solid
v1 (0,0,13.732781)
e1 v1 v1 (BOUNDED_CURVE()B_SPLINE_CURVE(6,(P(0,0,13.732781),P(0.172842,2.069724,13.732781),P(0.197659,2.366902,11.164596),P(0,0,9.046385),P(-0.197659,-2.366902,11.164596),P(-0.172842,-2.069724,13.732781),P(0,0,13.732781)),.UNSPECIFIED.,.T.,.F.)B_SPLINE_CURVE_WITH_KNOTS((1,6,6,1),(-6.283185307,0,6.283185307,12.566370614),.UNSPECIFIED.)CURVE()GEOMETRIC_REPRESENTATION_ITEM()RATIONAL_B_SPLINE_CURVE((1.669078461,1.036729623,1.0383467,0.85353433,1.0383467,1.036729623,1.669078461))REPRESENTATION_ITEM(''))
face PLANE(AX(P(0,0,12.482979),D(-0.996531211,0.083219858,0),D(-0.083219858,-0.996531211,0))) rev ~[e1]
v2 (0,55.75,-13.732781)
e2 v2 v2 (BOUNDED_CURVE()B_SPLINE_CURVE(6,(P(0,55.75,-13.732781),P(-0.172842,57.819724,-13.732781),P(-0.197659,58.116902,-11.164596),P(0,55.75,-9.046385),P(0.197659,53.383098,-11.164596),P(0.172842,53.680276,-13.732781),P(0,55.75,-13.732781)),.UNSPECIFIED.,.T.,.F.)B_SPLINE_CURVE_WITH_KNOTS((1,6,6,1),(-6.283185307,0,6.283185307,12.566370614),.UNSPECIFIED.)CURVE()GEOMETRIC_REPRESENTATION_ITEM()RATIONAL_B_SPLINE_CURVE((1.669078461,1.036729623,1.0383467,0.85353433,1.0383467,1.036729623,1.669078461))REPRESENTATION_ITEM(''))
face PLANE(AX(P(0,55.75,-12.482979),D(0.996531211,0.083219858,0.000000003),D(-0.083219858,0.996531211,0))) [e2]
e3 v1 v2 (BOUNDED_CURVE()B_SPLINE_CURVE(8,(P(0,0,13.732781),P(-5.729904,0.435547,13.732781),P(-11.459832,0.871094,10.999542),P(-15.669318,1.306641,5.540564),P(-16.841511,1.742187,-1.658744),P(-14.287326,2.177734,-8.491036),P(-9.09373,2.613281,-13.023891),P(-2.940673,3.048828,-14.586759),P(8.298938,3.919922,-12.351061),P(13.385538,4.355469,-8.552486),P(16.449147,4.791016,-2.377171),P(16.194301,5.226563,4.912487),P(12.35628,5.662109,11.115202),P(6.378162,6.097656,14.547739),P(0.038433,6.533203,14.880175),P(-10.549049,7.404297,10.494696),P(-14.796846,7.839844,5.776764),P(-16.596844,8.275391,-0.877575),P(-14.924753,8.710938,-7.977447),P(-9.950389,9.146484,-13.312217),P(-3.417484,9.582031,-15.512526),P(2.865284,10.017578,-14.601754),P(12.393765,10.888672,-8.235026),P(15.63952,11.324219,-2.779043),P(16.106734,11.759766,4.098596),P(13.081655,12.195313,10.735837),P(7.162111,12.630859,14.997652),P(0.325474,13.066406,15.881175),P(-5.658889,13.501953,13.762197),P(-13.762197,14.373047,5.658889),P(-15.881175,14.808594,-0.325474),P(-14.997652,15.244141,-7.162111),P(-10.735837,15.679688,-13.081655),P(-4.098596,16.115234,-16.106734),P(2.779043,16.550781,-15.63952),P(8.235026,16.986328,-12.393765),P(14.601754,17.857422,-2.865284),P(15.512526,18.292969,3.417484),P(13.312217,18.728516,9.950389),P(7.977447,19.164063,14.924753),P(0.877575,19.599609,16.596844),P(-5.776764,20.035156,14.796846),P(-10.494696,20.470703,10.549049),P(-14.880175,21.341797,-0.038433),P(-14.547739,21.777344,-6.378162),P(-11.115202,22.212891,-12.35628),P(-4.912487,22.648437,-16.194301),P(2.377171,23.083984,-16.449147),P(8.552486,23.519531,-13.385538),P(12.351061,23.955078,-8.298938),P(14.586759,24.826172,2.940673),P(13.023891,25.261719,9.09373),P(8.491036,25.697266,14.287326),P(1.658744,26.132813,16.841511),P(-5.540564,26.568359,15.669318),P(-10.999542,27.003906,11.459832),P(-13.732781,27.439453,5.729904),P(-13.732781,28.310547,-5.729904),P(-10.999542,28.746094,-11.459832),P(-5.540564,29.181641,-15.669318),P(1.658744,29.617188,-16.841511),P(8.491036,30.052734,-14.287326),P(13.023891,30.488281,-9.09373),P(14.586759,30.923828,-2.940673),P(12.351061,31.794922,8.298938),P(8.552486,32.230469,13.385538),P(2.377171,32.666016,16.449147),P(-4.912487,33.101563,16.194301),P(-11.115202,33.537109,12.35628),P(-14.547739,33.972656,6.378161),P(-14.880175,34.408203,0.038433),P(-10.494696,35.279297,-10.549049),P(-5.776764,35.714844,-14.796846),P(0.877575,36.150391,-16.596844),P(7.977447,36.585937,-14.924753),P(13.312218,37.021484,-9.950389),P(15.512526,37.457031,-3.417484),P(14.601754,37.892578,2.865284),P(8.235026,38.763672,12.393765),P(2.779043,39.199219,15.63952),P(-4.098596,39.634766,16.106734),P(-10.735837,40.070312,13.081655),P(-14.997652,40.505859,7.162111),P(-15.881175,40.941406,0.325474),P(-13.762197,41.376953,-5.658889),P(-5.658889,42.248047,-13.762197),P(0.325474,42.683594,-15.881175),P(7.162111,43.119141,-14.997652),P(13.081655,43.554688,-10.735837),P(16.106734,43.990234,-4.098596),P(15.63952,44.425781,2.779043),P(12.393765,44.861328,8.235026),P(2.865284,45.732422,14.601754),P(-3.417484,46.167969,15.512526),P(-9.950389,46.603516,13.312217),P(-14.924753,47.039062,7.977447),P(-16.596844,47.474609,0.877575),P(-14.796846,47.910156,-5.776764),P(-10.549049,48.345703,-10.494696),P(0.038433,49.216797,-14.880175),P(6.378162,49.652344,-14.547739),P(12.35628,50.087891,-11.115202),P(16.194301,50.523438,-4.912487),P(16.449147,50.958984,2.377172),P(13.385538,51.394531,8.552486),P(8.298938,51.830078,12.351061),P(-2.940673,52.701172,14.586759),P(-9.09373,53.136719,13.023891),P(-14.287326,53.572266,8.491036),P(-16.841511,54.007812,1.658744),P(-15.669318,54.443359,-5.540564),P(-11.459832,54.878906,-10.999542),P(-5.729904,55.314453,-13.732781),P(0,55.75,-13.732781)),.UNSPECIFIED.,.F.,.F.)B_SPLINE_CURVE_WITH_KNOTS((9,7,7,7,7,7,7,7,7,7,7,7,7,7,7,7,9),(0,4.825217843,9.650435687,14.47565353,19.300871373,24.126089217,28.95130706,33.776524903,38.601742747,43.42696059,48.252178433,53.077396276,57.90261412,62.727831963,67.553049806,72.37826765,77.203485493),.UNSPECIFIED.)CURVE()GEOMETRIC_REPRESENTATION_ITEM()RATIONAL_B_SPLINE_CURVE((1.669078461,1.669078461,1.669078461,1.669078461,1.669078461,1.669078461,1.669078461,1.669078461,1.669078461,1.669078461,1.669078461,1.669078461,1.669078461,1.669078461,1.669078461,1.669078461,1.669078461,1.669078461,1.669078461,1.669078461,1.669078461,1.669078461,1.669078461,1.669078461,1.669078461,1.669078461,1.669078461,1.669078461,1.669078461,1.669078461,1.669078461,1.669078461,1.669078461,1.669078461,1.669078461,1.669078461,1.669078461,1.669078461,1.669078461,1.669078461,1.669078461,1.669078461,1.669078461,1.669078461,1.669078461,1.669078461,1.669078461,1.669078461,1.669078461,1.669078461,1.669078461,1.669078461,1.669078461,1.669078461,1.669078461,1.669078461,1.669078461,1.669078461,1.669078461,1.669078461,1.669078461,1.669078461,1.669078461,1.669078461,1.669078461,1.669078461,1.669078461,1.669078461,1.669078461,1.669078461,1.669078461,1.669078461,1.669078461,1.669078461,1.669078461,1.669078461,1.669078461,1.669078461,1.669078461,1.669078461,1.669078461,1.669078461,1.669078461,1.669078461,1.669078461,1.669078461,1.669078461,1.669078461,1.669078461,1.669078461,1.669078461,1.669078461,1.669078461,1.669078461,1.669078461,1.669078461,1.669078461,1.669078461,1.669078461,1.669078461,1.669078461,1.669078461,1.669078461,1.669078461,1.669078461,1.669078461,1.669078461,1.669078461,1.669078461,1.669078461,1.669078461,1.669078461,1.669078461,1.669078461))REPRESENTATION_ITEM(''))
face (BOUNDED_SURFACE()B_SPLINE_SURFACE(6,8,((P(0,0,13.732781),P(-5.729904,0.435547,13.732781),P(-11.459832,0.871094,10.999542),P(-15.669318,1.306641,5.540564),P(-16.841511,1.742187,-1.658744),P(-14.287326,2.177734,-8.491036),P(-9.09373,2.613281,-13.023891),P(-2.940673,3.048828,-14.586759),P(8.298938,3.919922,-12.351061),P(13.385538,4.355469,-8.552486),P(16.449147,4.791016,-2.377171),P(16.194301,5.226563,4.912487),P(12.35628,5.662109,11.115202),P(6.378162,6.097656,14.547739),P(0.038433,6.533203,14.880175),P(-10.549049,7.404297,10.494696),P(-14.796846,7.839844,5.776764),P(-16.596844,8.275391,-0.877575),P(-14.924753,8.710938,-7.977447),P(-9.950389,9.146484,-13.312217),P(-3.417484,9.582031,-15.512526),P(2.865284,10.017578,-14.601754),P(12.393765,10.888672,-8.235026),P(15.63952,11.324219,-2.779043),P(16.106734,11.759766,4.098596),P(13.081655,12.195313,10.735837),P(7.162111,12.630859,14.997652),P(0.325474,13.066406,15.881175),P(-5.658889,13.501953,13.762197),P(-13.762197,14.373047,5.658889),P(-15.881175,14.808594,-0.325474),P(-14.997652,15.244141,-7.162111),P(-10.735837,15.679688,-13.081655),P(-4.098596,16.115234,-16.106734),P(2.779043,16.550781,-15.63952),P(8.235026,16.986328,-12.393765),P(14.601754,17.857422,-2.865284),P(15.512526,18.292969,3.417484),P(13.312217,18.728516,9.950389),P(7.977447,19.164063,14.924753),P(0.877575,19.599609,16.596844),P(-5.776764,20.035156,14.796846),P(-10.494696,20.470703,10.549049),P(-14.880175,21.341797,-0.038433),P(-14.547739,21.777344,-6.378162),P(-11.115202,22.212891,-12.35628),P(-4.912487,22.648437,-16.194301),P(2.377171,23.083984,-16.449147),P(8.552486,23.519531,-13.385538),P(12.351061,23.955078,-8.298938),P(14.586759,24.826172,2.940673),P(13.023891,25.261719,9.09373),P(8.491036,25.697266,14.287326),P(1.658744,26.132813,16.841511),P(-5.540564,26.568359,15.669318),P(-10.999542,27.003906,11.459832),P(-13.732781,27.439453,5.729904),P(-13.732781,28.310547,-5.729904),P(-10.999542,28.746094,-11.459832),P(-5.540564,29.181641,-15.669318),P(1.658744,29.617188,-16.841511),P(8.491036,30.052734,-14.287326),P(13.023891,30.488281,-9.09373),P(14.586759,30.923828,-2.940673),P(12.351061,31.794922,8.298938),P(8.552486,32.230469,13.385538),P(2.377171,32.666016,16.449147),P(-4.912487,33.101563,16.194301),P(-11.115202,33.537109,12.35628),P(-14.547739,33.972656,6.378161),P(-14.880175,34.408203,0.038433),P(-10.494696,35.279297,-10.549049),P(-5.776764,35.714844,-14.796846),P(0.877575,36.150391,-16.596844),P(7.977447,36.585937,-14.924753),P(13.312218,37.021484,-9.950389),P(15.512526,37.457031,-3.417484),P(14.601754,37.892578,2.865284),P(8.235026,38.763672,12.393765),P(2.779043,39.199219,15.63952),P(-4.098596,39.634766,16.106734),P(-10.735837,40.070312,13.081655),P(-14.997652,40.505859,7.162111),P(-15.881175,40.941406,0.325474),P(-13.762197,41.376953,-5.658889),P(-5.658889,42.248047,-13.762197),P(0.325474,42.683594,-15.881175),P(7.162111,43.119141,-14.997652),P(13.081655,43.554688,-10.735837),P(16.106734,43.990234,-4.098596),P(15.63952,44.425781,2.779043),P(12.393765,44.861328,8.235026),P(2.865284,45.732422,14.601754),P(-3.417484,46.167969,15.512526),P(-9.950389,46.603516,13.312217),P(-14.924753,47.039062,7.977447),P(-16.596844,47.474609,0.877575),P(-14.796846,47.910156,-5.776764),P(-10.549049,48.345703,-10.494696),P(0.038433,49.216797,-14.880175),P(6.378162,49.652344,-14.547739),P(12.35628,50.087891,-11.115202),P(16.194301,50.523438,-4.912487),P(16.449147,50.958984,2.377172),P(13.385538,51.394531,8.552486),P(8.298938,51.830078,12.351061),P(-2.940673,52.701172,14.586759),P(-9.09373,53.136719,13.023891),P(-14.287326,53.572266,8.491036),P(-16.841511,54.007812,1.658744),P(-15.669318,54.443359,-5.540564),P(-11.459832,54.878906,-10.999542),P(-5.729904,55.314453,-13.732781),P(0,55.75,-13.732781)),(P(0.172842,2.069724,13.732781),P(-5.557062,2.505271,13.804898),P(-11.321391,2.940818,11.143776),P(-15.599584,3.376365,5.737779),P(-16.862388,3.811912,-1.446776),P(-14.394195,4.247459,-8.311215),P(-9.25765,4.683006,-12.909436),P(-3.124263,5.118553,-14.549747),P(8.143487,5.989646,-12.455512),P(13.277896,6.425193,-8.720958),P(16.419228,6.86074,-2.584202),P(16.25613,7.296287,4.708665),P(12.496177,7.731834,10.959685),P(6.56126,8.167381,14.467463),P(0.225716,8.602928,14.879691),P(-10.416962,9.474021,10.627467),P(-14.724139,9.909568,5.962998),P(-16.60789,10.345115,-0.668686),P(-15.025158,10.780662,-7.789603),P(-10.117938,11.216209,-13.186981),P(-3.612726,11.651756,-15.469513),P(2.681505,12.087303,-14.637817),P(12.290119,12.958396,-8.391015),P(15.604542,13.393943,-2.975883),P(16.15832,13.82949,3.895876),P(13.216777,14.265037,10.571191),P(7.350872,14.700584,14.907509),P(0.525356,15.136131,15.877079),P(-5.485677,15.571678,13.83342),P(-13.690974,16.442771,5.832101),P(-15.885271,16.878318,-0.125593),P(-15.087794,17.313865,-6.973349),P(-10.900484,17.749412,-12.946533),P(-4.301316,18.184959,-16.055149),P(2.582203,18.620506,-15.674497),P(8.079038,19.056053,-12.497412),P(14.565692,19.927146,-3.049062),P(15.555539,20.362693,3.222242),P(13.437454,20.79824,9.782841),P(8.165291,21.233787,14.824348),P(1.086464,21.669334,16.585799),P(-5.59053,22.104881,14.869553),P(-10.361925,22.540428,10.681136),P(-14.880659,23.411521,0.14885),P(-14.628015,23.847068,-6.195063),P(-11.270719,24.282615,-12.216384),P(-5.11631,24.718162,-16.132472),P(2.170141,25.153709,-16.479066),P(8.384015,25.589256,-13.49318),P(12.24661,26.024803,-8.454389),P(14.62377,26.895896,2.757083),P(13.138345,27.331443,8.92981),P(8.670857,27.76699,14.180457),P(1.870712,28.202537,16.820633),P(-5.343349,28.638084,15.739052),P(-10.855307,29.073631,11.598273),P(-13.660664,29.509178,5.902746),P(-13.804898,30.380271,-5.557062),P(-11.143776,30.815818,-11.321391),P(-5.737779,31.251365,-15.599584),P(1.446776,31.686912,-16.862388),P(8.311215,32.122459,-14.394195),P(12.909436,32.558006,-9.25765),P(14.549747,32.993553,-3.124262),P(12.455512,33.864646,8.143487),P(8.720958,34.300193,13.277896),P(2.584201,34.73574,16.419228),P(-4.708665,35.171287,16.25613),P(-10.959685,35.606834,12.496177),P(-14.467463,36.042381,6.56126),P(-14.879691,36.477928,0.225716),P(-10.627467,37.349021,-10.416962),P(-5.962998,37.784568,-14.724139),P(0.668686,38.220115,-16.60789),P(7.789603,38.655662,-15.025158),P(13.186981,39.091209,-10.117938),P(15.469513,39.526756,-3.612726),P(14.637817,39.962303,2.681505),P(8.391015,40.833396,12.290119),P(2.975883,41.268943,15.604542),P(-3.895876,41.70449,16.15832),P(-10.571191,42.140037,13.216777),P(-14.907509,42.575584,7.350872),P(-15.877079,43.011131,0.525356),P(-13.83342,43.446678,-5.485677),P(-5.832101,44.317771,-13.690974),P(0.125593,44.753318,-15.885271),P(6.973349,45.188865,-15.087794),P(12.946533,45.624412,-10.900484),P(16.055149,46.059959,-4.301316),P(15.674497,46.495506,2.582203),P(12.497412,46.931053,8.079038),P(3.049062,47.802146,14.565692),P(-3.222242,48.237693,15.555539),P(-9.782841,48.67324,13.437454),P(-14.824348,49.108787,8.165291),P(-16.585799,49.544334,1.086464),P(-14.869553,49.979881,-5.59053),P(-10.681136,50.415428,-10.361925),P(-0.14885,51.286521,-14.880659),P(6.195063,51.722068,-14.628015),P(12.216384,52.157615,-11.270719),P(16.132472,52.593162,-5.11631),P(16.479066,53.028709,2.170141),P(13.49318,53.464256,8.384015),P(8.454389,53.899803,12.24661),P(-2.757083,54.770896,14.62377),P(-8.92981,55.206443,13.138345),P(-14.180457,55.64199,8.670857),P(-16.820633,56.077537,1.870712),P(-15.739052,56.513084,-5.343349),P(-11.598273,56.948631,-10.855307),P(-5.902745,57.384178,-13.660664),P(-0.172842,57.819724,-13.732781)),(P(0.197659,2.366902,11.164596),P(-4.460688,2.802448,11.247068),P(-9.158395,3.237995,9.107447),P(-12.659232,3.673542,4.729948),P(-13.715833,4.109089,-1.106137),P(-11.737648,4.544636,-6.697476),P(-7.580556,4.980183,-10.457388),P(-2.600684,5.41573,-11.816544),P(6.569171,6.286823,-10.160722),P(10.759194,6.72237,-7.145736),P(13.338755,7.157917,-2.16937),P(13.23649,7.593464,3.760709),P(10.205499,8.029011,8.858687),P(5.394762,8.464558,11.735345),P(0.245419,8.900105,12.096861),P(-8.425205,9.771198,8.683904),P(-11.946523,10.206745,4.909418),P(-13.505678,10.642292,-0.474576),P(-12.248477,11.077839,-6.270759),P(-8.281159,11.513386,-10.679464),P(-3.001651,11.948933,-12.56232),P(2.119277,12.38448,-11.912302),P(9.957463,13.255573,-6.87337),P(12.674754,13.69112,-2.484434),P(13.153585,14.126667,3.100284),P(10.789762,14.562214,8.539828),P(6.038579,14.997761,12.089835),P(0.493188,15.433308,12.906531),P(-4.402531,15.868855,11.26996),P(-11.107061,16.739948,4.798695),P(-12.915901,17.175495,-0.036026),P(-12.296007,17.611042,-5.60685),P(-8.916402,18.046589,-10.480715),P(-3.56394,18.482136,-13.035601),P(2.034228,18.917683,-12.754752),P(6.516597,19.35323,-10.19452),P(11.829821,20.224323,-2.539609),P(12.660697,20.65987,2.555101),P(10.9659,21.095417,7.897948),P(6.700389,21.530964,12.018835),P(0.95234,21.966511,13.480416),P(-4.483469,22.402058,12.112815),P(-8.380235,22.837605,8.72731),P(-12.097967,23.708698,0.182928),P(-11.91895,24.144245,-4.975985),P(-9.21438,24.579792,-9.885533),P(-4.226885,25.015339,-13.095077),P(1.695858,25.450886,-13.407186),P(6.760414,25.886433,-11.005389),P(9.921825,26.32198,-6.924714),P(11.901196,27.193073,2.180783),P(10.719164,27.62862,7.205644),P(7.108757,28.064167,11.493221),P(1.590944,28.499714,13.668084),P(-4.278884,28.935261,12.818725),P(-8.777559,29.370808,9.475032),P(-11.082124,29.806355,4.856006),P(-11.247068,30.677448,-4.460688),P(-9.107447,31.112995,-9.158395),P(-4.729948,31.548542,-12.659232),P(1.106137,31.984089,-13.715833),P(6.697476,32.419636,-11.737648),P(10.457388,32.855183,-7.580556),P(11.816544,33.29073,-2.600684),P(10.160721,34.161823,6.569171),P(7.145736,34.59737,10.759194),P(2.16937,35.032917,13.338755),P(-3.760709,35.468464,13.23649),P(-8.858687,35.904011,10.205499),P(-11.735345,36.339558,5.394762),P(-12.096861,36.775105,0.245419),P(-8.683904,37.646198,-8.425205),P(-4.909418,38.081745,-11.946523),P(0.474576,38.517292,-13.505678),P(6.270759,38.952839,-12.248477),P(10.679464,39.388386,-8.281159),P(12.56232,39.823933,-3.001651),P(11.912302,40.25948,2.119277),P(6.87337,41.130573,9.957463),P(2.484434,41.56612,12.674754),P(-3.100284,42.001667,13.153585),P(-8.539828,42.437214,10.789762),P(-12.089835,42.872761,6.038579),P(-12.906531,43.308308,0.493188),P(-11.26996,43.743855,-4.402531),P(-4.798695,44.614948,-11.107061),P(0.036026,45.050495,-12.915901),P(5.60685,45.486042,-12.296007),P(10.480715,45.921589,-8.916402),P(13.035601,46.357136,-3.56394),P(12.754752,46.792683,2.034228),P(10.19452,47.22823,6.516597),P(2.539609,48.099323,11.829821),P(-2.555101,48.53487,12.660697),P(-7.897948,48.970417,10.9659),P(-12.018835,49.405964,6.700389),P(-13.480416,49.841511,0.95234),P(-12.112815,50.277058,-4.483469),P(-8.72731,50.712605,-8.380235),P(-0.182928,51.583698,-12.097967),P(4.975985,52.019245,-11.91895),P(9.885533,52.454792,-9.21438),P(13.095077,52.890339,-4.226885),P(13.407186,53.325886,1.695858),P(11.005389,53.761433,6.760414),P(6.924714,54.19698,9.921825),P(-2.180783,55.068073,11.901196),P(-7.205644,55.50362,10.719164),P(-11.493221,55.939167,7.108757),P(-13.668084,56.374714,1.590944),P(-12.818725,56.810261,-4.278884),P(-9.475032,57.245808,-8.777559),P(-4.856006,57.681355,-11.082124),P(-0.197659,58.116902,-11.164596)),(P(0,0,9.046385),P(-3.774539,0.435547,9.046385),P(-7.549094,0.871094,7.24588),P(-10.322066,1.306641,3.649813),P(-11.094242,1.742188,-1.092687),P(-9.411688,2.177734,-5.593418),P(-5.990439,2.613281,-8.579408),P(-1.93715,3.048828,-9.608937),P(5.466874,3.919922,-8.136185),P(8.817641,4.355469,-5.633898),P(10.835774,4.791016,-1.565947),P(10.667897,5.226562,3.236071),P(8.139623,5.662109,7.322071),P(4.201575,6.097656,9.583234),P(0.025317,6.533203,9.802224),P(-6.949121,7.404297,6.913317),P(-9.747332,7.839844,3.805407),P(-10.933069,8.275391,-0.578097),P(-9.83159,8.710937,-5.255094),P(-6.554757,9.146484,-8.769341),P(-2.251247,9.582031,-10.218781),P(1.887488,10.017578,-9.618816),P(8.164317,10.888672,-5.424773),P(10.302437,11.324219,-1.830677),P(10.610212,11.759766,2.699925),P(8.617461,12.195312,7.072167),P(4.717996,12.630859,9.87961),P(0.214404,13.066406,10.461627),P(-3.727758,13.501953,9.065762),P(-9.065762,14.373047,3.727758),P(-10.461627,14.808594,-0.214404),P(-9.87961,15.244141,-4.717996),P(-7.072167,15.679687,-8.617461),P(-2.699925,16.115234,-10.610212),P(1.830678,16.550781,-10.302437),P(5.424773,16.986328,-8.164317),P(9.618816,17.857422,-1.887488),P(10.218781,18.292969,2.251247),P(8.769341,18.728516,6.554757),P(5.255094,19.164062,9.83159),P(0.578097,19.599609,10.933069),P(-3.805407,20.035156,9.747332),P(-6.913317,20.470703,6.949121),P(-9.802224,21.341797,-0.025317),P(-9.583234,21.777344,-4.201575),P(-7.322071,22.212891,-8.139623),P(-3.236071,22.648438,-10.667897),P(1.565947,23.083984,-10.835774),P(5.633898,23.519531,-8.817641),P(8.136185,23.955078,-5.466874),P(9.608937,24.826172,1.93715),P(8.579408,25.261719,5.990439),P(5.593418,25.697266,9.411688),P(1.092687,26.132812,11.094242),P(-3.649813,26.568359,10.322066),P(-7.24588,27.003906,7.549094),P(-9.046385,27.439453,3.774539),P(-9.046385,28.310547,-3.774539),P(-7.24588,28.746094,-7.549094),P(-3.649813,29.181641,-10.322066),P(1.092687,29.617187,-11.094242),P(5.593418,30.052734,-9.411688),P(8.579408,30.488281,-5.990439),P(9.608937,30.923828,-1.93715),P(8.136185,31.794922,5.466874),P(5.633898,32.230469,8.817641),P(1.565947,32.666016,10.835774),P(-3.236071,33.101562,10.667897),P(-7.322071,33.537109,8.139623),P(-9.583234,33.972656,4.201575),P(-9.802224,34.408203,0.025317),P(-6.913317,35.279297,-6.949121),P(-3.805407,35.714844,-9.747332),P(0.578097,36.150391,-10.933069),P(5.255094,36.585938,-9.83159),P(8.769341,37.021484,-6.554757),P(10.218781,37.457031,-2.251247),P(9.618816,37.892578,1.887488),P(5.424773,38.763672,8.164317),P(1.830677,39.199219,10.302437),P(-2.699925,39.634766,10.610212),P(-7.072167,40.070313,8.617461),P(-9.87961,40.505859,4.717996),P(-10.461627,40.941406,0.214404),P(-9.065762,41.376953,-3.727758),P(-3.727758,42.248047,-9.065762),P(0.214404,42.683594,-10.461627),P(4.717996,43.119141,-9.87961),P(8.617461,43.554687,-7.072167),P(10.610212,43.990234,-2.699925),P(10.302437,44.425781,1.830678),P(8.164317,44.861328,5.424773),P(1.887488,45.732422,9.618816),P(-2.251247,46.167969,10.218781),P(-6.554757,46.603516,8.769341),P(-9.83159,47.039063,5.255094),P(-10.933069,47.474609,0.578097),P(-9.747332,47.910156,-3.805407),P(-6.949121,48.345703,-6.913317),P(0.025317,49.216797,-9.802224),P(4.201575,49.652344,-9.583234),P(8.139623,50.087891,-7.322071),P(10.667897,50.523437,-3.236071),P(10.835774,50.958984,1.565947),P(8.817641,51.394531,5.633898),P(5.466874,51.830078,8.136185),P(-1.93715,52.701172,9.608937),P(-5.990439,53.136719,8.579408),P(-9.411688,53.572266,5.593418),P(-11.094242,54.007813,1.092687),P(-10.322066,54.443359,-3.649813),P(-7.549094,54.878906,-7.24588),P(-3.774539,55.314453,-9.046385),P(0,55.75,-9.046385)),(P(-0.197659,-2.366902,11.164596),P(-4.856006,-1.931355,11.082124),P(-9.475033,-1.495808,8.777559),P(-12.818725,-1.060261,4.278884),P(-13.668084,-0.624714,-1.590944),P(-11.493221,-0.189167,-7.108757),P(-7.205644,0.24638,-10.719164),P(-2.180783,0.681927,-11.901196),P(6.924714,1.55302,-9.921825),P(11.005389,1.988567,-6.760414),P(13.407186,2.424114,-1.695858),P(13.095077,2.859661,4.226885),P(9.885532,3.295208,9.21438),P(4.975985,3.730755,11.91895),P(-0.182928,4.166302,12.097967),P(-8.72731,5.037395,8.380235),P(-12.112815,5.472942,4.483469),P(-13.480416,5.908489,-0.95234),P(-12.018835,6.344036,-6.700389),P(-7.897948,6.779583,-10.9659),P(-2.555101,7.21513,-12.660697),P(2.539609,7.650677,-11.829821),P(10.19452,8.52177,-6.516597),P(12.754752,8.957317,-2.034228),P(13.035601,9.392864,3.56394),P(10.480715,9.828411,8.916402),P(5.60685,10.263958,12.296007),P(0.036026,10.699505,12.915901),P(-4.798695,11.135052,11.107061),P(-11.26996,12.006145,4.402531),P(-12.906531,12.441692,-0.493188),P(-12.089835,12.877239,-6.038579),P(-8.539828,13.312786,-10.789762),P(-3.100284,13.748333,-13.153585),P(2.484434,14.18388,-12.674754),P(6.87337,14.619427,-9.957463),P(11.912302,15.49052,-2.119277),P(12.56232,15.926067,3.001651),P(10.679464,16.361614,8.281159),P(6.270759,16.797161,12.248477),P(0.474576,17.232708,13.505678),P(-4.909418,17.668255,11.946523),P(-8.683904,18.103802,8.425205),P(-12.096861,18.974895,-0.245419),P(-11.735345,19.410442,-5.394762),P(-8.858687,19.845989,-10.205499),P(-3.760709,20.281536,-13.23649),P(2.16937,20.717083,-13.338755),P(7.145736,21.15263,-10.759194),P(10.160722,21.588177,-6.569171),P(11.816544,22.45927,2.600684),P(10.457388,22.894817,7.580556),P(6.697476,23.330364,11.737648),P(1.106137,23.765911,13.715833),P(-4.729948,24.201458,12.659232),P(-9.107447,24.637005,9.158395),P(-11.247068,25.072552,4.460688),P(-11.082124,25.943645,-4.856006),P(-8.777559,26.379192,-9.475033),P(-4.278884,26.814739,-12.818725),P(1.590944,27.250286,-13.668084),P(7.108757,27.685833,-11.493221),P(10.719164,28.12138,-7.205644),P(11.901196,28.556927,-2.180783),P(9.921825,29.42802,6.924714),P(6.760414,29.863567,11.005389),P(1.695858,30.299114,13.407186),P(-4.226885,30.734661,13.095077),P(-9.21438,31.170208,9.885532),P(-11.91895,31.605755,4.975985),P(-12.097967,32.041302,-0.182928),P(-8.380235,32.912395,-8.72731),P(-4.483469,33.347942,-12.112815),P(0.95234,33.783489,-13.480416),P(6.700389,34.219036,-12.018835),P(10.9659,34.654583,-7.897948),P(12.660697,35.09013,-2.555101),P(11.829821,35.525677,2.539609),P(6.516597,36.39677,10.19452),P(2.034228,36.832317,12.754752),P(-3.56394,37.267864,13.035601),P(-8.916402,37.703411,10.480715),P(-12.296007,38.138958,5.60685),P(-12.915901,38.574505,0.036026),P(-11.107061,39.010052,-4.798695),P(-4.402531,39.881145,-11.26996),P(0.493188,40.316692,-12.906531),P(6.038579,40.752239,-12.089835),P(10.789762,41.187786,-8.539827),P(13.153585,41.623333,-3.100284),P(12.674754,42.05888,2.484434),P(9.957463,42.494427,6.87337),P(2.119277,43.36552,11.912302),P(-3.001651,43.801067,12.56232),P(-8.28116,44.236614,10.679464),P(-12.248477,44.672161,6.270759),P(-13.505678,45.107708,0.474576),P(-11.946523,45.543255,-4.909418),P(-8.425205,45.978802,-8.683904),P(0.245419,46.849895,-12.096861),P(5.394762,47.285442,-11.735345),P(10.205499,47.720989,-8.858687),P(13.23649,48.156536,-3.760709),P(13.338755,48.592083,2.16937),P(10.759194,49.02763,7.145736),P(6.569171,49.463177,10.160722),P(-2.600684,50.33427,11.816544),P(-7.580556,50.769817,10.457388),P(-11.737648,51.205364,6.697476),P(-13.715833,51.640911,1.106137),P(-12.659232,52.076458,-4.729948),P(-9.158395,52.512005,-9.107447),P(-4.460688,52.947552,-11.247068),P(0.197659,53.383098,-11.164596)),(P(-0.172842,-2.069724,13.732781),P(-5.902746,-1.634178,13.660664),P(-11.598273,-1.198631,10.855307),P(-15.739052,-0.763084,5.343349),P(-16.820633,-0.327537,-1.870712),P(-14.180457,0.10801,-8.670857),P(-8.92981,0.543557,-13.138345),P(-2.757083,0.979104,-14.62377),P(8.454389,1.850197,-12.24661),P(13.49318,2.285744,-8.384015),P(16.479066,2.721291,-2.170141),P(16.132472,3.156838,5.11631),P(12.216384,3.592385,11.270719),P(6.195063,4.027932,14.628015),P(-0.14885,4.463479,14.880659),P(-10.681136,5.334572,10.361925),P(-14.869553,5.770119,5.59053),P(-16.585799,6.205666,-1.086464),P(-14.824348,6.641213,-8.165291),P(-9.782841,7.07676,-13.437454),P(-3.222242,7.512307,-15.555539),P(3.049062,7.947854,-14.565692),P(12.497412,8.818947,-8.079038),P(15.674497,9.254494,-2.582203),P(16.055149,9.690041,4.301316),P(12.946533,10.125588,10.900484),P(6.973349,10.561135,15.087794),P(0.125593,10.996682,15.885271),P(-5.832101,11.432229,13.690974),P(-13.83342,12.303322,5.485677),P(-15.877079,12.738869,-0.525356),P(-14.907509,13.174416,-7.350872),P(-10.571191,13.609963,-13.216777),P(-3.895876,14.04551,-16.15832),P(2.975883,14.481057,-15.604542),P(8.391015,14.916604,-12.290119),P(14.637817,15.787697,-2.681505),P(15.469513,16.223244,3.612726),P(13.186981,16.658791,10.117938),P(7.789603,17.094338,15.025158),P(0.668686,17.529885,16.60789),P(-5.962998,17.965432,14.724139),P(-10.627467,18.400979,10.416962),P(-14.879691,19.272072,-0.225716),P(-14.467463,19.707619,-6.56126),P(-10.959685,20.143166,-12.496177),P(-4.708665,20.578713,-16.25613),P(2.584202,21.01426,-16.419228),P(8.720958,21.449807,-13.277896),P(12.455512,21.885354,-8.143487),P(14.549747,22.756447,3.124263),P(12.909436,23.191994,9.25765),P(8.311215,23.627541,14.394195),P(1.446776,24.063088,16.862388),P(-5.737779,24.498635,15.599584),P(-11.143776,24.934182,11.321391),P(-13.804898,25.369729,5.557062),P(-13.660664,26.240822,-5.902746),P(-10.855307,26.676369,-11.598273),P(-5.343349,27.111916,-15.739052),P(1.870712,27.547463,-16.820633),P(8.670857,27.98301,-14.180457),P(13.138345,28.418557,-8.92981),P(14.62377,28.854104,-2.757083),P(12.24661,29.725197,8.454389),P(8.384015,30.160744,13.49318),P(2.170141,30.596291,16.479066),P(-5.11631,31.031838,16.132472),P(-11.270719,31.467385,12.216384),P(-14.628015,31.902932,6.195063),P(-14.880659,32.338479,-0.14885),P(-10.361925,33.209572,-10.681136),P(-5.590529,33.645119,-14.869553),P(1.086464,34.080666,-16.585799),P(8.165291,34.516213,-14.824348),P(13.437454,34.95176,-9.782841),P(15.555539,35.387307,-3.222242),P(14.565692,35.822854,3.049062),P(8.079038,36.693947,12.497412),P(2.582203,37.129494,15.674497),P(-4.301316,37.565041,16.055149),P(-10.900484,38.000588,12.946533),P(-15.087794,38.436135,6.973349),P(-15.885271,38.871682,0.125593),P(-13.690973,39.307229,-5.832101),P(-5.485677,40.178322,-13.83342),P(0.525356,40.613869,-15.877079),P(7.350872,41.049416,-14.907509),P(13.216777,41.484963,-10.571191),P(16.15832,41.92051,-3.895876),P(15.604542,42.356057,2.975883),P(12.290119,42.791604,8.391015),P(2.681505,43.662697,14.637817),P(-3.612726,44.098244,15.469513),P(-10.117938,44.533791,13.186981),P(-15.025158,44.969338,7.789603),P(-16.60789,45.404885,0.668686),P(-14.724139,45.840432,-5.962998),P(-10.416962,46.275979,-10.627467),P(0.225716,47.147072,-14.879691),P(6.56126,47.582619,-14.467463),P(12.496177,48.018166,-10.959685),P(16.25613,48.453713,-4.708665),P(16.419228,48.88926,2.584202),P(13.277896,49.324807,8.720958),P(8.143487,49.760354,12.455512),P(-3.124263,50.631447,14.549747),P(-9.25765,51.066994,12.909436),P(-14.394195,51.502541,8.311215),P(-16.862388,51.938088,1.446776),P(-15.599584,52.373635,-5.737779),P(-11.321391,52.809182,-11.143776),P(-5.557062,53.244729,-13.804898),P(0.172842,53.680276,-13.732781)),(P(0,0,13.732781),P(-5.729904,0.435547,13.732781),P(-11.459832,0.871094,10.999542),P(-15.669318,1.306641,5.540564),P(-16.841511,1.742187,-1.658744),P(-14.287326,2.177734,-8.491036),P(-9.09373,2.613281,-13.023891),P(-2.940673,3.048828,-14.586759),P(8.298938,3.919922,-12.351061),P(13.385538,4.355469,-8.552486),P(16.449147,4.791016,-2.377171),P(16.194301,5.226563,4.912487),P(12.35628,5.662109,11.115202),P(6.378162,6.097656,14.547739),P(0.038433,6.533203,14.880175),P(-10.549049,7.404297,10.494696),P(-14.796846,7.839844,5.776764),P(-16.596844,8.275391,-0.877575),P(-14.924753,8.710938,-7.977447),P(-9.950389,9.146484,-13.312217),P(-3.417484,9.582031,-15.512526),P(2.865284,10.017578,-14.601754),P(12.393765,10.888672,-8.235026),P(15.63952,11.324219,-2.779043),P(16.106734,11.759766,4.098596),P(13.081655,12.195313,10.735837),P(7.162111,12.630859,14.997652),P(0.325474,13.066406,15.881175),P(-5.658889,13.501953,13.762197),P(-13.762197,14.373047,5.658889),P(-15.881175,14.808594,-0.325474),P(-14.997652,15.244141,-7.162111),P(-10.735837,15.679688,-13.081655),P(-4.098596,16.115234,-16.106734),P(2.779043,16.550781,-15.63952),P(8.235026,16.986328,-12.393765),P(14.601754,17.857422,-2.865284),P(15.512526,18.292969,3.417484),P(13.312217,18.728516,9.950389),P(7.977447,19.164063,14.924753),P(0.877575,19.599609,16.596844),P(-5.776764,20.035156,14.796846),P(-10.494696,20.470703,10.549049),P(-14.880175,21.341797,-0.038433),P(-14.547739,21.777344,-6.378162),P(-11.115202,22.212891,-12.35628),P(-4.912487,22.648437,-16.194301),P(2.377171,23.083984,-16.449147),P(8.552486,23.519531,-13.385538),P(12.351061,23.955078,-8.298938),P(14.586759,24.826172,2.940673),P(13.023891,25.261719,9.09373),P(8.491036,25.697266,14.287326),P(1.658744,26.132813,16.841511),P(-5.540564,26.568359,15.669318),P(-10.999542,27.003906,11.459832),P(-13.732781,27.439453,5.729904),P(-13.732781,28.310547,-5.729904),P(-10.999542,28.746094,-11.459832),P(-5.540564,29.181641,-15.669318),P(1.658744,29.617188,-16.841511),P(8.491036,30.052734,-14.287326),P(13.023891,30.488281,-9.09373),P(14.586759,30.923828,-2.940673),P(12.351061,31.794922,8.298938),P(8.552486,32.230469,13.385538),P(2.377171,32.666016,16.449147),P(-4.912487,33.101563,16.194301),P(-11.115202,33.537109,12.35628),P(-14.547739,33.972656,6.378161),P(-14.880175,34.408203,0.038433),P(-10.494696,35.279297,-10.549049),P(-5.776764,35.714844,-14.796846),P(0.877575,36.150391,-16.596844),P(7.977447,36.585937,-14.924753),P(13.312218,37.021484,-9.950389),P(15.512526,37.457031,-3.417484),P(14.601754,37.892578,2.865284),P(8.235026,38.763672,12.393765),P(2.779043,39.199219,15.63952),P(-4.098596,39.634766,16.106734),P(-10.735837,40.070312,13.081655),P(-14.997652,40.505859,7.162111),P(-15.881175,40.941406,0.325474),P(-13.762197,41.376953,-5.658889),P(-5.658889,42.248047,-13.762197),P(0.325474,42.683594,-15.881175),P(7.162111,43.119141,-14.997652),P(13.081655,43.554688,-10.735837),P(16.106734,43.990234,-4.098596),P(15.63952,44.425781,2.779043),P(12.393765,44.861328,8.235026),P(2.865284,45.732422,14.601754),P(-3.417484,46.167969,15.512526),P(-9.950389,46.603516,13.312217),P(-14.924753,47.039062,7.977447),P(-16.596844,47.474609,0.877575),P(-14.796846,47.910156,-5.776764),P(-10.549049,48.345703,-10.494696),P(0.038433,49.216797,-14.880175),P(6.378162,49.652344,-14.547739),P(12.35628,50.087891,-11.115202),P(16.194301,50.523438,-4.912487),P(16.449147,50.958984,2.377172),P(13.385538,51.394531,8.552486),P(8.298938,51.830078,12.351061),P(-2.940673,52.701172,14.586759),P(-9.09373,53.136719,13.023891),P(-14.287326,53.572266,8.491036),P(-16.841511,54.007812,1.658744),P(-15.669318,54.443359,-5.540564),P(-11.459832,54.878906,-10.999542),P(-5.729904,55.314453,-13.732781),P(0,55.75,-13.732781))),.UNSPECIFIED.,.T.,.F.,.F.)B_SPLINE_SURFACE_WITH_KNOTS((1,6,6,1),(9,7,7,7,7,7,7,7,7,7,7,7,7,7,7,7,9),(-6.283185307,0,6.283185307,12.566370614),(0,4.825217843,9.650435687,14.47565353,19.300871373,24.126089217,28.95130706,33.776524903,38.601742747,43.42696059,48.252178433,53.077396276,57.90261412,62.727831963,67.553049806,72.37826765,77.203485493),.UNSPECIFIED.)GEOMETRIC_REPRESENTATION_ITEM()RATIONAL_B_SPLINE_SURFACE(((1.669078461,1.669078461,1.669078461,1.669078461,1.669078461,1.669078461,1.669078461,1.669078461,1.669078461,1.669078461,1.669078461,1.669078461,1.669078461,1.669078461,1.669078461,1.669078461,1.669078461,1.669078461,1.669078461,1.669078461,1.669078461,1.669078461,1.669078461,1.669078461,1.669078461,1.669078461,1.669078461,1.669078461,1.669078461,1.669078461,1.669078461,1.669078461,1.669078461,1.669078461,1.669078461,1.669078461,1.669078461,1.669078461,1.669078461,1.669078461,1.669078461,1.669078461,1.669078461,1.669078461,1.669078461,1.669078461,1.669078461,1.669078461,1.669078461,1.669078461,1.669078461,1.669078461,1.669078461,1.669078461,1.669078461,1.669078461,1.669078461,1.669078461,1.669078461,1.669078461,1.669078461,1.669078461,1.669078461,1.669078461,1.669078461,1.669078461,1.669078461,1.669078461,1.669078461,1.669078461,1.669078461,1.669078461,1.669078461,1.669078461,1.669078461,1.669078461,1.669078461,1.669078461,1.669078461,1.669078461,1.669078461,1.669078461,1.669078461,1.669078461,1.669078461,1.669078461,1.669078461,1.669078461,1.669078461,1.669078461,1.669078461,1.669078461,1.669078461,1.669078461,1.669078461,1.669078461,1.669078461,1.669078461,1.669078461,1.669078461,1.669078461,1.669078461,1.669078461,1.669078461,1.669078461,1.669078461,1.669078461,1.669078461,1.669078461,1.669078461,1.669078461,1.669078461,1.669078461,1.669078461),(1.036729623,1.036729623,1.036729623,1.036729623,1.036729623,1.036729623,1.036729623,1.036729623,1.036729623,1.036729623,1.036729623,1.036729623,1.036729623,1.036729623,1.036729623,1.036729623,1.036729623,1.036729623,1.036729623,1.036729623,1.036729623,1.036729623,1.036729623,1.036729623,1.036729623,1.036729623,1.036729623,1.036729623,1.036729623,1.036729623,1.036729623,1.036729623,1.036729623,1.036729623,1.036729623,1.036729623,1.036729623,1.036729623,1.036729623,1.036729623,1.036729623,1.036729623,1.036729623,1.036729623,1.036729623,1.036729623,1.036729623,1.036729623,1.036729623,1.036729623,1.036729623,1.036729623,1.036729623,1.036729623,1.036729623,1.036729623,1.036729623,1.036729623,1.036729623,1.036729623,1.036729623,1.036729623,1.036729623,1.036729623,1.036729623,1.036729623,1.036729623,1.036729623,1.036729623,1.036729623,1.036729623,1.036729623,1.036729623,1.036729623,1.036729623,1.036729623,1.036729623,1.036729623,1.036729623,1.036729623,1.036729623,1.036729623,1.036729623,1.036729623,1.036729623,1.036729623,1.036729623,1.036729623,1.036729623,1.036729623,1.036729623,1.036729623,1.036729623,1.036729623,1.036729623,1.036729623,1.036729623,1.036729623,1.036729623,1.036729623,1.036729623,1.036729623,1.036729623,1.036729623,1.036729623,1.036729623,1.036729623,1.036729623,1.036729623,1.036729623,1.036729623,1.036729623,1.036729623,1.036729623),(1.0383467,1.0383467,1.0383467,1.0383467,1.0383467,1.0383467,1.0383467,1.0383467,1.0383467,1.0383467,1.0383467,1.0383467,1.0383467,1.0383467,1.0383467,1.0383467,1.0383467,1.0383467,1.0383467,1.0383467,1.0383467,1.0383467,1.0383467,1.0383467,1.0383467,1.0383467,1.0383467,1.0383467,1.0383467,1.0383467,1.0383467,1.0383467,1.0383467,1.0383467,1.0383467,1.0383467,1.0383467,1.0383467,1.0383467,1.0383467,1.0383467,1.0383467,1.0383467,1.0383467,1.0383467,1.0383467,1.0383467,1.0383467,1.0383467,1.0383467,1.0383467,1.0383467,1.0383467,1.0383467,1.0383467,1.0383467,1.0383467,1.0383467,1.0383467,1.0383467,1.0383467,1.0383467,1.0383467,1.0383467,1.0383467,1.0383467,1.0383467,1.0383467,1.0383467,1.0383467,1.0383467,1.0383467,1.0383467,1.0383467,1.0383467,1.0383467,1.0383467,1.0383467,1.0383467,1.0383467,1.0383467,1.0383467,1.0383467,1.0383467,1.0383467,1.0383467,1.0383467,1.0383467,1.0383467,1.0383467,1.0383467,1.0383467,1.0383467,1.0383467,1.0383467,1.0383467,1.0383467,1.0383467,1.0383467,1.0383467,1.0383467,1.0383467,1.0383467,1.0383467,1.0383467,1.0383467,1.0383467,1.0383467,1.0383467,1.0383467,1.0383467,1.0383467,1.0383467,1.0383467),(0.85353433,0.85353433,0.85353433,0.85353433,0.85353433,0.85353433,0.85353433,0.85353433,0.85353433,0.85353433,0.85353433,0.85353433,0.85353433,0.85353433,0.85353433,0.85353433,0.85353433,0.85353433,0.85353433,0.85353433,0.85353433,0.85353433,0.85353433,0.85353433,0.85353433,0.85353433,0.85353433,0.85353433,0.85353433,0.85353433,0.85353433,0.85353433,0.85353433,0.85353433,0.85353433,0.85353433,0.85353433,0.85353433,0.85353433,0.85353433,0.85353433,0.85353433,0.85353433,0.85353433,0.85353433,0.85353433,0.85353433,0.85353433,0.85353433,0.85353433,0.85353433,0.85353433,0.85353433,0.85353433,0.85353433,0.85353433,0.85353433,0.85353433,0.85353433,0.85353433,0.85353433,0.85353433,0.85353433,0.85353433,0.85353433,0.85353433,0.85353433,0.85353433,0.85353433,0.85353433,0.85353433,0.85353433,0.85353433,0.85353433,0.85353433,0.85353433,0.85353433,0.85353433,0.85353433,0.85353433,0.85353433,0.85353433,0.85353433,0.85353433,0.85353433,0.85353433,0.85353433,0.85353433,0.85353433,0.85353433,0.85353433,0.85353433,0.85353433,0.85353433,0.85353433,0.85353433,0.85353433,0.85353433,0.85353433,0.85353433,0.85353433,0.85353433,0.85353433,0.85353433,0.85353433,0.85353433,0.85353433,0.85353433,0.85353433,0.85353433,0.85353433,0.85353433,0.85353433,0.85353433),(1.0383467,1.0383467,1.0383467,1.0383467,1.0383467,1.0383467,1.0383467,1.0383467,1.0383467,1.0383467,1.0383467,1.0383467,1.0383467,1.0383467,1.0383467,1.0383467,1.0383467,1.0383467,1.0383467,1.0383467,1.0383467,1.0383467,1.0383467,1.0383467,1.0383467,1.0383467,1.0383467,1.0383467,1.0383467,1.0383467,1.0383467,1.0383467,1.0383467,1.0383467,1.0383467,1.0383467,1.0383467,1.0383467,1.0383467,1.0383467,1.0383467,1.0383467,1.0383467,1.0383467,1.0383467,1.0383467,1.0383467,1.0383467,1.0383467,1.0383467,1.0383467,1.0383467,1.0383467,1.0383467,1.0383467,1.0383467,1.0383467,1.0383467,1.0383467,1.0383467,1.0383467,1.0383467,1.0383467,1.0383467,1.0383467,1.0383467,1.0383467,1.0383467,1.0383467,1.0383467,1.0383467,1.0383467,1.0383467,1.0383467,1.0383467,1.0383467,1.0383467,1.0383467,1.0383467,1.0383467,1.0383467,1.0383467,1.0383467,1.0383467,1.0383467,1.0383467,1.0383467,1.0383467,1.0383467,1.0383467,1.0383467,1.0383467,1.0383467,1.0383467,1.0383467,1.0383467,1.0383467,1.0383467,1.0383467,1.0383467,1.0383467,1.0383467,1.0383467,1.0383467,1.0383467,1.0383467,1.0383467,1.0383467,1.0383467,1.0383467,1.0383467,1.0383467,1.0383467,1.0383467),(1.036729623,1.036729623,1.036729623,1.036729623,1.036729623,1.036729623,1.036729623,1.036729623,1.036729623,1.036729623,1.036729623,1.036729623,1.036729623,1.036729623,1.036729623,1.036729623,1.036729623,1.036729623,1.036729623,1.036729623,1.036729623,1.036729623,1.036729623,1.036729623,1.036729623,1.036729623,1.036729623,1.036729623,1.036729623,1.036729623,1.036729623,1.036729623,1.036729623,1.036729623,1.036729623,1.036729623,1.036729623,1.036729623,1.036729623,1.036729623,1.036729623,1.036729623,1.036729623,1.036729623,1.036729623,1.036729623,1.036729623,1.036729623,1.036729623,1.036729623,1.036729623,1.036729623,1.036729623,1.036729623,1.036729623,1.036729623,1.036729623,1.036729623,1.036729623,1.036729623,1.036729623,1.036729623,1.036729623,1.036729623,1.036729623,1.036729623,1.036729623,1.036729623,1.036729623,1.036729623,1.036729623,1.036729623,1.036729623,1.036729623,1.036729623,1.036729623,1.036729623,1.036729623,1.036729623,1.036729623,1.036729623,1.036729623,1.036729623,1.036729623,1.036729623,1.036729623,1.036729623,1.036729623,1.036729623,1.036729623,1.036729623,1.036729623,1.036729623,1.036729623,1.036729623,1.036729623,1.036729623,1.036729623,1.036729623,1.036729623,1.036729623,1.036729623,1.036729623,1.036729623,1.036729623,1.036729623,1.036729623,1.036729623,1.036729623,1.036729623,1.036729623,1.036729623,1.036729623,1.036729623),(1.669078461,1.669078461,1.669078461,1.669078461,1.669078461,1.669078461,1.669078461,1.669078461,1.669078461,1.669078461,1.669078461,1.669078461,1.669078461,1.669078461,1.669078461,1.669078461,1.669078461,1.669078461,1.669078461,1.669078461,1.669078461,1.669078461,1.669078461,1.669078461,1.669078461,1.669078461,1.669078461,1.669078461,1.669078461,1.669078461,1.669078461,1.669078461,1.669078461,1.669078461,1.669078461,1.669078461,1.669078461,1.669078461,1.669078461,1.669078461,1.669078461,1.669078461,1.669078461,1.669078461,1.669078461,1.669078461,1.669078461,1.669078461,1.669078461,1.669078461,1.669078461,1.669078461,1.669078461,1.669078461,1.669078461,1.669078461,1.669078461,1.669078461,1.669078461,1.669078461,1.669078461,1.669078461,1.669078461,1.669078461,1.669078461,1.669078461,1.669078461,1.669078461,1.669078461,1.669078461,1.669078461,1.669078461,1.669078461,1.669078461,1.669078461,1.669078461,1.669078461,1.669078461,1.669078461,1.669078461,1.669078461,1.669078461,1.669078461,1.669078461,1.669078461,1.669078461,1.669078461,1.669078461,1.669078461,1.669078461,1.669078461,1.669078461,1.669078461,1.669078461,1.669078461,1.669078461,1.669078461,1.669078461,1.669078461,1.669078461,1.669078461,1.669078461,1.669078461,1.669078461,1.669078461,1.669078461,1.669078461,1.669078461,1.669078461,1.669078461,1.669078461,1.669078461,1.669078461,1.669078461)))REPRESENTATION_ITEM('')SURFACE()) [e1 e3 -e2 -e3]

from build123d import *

# Parameters (mm, degrees)
SWEEP1_PITCH  = 6.558823529
SWEEP1_HEIGHT = 55.75
SWEEP1_RADIUS = 12.5
SKETCH2_R     = 1.25


with BuildPart() as part:
    # Sweep1: sweep along a helix
    with BuildLine() as sweep1_path:
        Helix(SWEEP1_PITCH, SWEEP1_HEIGHT, SWEEP1_RADIUS, center=(0, 0, 0), direction=(0, 1, 0), lefthand=True)
    # Sketch2 → Sweep1 (sweep)
    with BuildSketch(Plane(origin=(0, 0, 12.5), x_dir=(0, 0, 1), z_dir=(-0.9965312113765106, 0.08321985792143866, 1.3822626039964883e-14))):
        with Locations((-0.017218635, 0)):
            Circle(SKETCH2_R)
    sweep(path=sweep1_path.line, is_frenet=True)


solid = part.part
